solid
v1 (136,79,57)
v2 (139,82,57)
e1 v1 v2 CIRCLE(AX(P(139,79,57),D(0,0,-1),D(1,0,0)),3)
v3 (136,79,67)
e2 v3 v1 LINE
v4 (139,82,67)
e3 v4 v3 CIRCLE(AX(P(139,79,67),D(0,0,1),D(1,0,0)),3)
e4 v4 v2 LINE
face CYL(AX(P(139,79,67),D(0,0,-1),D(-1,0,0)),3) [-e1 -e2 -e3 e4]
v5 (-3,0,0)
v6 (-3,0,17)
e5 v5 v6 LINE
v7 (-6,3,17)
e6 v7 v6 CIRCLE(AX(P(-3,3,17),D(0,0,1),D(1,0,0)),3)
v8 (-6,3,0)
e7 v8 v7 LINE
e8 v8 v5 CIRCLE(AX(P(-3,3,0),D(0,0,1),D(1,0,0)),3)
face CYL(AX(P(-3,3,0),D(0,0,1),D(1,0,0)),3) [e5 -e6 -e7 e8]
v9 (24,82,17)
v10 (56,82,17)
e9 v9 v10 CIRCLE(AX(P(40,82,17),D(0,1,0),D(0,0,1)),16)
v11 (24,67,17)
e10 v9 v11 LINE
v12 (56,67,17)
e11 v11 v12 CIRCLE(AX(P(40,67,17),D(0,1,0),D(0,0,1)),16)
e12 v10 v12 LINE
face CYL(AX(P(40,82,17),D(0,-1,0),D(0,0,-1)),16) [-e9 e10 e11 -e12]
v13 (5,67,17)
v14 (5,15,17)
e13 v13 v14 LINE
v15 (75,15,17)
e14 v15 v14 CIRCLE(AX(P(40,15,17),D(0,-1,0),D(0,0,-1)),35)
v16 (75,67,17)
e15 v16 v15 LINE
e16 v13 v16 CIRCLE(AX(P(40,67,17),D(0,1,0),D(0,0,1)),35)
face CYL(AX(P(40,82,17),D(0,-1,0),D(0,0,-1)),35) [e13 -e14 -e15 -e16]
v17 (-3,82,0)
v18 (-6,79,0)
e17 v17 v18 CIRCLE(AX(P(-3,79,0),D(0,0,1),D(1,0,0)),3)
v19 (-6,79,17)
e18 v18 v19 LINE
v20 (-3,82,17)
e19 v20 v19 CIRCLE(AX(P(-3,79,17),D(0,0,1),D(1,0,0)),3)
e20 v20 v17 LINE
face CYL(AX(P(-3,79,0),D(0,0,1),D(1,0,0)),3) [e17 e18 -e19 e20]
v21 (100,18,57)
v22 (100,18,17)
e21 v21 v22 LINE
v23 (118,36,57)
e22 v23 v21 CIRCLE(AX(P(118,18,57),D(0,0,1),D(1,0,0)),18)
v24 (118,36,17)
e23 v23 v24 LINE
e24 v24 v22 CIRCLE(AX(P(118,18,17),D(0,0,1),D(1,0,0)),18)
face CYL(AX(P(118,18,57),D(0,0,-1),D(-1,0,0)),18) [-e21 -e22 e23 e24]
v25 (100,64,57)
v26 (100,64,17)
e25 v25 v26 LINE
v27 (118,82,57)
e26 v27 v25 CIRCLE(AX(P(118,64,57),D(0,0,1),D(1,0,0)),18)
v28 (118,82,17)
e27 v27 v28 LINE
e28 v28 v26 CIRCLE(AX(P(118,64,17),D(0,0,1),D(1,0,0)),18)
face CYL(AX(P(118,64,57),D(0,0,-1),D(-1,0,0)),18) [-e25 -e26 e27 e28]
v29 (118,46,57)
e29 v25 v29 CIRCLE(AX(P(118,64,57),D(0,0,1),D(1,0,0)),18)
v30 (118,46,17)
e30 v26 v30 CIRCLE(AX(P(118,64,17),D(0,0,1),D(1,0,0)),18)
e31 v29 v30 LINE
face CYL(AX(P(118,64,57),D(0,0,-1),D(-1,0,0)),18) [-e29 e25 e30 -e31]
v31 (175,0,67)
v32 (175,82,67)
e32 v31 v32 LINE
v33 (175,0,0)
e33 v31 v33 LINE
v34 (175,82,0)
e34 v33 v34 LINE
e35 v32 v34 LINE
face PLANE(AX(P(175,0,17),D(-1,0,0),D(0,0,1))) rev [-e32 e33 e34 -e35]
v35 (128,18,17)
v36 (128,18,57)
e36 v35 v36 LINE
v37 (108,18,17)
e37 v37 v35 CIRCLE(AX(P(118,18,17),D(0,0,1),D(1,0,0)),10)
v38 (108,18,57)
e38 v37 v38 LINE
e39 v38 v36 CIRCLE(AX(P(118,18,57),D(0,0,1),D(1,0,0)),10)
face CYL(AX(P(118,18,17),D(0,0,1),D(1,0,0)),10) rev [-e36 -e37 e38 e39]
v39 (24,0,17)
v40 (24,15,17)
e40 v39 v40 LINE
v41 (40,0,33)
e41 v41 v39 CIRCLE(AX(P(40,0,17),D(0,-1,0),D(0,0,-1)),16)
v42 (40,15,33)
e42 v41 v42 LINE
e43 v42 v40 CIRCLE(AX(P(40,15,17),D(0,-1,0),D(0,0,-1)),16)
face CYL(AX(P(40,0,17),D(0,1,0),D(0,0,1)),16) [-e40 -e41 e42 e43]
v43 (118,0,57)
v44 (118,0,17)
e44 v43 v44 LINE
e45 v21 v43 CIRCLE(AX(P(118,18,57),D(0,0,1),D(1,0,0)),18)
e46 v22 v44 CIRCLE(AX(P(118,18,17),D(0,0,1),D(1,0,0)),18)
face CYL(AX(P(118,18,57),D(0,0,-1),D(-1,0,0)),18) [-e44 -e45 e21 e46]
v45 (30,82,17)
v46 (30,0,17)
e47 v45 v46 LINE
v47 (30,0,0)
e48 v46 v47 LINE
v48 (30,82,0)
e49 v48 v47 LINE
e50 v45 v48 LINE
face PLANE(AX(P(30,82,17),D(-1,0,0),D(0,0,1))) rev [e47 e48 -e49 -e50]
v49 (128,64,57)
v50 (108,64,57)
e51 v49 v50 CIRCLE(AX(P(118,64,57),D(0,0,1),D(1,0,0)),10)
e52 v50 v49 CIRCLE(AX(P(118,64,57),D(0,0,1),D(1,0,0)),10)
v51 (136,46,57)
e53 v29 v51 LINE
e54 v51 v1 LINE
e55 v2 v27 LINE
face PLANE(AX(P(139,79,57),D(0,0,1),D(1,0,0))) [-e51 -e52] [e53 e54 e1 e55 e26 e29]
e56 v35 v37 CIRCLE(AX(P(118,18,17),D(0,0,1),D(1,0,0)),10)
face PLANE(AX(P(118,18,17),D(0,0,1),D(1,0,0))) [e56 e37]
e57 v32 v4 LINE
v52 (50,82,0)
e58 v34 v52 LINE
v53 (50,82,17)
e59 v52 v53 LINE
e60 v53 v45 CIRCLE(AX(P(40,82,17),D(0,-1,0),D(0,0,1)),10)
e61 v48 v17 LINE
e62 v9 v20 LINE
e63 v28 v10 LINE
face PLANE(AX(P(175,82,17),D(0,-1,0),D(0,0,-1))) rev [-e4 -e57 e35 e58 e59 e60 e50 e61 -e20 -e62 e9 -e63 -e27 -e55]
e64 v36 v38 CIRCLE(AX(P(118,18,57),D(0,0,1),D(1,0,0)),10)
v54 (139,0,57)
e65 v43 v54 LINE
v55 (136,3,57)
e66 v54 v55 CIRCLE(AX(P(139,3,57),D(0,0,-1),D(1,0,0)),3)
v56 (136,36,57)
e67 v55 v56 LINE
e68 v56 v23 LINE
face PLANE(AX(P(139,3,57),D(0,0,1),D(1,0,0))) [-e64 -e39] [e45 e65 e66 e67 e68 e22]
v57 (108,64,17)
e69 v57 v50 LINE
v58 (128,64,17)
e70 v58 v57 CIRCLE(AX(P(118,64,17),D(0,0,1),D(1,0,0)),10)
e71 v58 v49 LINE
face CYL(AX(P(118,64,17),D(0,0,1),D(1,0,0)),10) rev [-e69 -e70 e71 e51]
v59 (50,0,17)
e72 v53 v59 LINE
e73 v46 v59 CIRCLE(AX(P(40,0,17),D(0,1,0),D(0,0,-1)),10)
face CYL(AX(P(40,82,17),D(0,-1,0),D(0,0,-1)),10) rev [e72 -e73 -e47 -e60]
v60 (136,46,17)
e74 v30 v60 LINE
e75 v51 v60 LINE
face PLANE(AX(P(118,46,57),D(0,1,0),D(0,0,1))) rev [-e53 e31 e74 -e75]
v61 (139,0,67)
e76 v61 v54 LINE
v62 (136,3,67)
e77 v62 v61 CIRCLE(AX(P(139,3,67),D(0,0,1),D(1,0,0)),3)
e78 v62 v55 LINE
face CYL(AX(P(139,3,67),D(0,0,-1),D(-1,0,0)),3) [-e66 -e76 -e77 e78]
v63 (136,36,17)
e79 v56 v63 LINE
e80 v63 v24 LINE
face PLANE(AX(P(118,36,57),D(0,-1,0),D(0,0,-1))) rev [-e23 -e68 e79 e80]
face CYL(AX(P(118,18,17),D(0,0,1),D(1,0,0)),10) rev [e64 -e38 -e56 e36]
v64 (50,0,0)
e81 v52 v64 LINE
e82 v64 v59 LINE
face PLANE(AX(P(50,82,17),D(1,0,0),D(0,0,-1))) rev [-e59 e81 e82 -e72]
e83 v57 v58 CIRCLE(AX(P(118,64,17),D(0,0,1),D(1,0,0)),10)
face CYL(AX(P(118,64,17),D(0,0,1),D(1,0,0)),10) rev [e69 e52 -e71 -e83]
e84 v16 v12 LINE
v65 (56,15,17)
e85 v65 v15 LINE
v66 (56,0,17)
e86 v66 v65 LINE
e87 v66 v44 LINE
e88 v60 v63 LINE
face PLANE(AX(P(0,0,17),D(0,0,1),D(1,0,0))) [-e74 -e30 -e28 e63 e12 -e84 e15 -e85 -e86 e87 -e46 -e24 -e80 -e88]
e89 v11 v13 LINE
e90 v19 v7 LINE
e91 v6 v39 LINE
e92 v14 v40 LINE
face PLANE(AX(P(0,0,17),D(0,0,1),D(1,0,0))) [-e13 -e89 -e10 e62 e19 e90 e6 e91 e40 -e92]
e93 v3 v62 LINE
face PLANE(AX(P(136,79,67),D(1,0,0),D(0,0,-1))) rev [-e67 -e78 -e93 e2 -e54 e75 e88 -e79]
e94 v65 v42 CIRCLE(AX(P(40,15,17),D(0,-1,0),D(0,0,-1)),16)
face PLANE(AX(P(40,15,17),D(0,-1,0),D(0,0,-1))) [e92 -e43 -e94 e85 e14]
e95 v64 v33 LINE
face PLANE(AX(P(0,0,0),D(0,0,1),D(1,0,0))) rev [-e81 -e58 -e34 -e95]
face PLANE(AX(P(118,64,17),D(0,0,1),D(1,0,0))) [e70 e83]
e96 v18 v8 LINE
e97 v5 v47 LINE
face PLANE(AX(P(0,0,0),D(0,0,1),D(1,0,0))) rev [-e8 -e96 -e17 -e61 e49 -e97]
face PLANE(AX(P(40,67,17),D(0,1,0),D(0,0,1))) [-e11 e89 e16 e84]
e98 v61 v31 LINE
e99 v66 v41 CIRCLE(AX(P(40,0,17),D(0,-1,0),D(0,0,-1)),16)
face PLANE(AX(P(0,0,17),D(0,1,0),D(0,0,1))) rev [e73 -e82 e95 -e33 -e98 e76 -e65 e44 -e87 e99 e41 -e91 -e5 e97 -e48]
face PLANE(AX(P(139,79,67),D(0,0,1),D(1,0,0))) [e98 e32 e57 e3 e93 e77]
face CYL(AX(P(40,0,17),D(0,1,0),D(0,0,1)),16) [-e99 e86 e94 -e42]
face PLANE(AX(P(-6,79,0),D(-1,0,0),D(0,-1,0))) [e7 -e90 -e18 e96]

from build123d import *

# Parameters (mm, degrees)
BASE_BLOCK_SKETCH_W       = 175
BASE_BLOCK_SKETCH_H       = 82
BASE_BLOCK_DEPTH          = 17
SIDE_WALL_DEPTH           = 50
STEP_PAD_SKETCH_W         = 17
STEP_PAD_SKETCH_H         = 82
STEP_PAD_DEPTH            = 3
RAISED_BLOCK_DEPTH        = 17
LUG_BOSS_DEPTH            = 82
LUG_PROFILE_CUT_DEPTH     = 82
KNUCKLE_SLOT_1_DEPTH      = 15
KNUCKLE_START             = -15
KNUCKLE_SLOT_2_DEPTH      = 15
KNUCKLE_RING_2_DEPTH      = 15
KNUCKLE_START_2           = 15
KNUCKLE_RING_1_DEPTH      = 15
CURVED_BRACKET_DEPTH      = 40
BRACKET_TRIM_CUT_SKETCH_R = 10
BRACKET_TRIM_CUT_DEPTH    = 40


with BuildPart() as part:
    # Base Block Sketch → Base Block (new body)
    with BuildSketch(Plane.XY):
        with Locations((87.5, 41)):
            Rectangle(BASE_BLOCK_SKETCH_W, BASE_BLOCK_SKETCH_H)
    extrude(amount=BASE_BLOCK_DEPTH)

    # Side Wall Sketch → Side Wall (add)
    with BuildSketch(Plane.XY.offset(17)):
        with BuildLine():
            Line((175, 82), (175, 0))
            Line((175, 0), (139, 0))
            ThreePointArc((139, 0), (136.878679656, 0.878679656), (136, 3))
            Line((136, 3), (136, 79))
            ThreePointArc((136, 79), (136.878679656, 81.121320344), (139, 82))
            Line((139, 82), (175, 82))
        make_face()
    extrude(amount=SIDE_WALL_DEPTH)

    # Step Pad Sketch → Step Pad (add)
    with BuildSketch(Plane.ZY):
        with Locations((8.5, 41)):
            Rectangle(STEP_PAD_SKETCH_W, STEP_PAD_SKETCH_H)
    extrude(amount=STEP_PAD_DEPTH)

    # Raised Block Sketch → Raised Block (add)
    with BuildSketch(Plane.XY.offset(17)):
        with BuildLine():
            Line((-3, 82), (-3, 0))
            ThreePointArc((-3, 0), (-5.121320344, 0.878679656), (-6, 3))
            Line((-6, 3), (-6, 79))
            ThreePointArc((-6, 79), (-5.121320344, 81.121320344), (-3, 82))
        make_face()
    extrude(amount=-RAISED_BLOCK_DEPTH)

    # Lug Boss Sketch → Lug Boss (add)
    with BuildSketch(Plane.XZ):
        with BuildLine():
            ThreePointArc((75, 17), (40, 52), (5, 17))
            Line((5, 17), (75, 17))
        make_face()
    extrude(amount=-LUG_BOSS_DEPTH)

    # Lug Profile Cut Sketch → Lug Profile Cut (cut)
    with BuildSketch(Plane.XZ):
        with BuildLine():
            Line((30, 0), (50, 0))
            Line((50, 0), (50, 17))
            ThreePointArc((50, 17), (40, 27), (30, 17))
            Line((30, 17), (30, 0))
        make_face()
    extrude(amount=-LUG_PROFILE_CUT_DEPTH, mode=Mode.SUBTRACT)

    # Knuckle Slot 1 Sketch → Knuckle Slot 1 (cut)
    with BuildSketch(Plane.XZ):
        with BuildLine():
            Line((5, 17), (30, 17))
            ThreePointArc((30, 17), (40, 27), (50, 17))
            Line((50, 17), (75, 17))
            ThreePointArc((75, 17), (40, 52), (5, 17))
        make_face()
    extrude(amount=-KNUCKLE_SLOT_1_DEPTH, mode=Mode.SUBTRACT)

    # Knuckle Slot 2 Sketch → Knuckle Slot 2 (cut)
    with BuildSketch(Plane(origin=(0, 82, 0), x_dir=(1, 0, 0), z_dir=(0, 1, 0)).offset(KNUCKLE_START)):
        with BuildLine():
            Line((30, -17), (5, -17))
            ThreePointArc((5, -17), (40, -52), (75, -17))
            Line((75, -17), (50, -17))
            ThreePointArc((50, -17), (40, -27), (30, -17))
        make_face()
    extrude(amount=KNUCKLE_SLOT_2_DEPTH, mode=Mode.SUBTRACT)

    # Knuckle Ring 2 Sketch → Knuckle Ring 2 (add)
    with BuildSketch(Plane(origin=(0, 67, 0), x_dir=(1, 0, 0), z_dir=(0, 1, 0))):
        with BuildLine():
            Line((24, -17), (30, -17))
            ThreePointArc((30, -17), (40, -27), (50, -17))
            Line((50, -17), (56, -17))
            ThreePointArc((56, -17), (40, -33), (24, -17))
        make_face()
    extrude(amount=KNUCKLE_RING_2_DEPTH)

    # Knuckle Ring 1 Sketch → Knuckle Ring 1 (add)
    with BuildSketch(Plane.XZ.offset(-15).offset(KNUCKLE_START_2)):
        with BuildLine():
            Line((24, 17), (30, 17))
            ThreePointArc((30, 17), (40, 27), (50, 17))
            Line((50, 17), (56, 17))
            ThreePointArc((56, 17), (40, 33), (24, 17))
        make_face()
    extrude(amount=-KNUCKLE_RING_1_DEPTH)

    # Curved Bracket Sketch → Curved Bracket (add)
    with BuildSketch(Plane.XY.offset(17)):
        with BuildLine():
            Line((118, 0), (139, 0))
            ThreePointArc((139, 0), (136.878679656, 0.878679656), (136, 3))
            Line((136, 3), (136, 36))
            Line((136, 36), (118, 36))
            ThreePointArc((118, 36), (100, 18), (118, 0))
        make_face()
        with BuildLine():
            Line((118, 82), (139, 82))
            ThreePointArc((139, 82), (136.878679656, 81.121320344), (136, 79))
            Line((136, 79), (136, 46))
            Line((136, 46), (118, 46))
            ThreePointArc((118, 46), (100, 64), (118, 82))
        make_face()
    extrude(amount=CURVED_BRACKET_DEPTH)

    # Bracket Trim Cut Sketch → Bracket Trim Cut (cut)
    with BuildSketch(Plane.XY.offset(57)):
        with Locations((118, 64)):
            Circle(BRACKET_TRIM_CUT_SKETCH_R)
        with Locations((118, 18)):
            Circle(BRACKET_TRIM_CUT_SKETCH_R)
    extrude(amount=-BRACKET_TRIM_CUT_DEPTH, mode=Mode.SUBTRACT)


solid = part.part
